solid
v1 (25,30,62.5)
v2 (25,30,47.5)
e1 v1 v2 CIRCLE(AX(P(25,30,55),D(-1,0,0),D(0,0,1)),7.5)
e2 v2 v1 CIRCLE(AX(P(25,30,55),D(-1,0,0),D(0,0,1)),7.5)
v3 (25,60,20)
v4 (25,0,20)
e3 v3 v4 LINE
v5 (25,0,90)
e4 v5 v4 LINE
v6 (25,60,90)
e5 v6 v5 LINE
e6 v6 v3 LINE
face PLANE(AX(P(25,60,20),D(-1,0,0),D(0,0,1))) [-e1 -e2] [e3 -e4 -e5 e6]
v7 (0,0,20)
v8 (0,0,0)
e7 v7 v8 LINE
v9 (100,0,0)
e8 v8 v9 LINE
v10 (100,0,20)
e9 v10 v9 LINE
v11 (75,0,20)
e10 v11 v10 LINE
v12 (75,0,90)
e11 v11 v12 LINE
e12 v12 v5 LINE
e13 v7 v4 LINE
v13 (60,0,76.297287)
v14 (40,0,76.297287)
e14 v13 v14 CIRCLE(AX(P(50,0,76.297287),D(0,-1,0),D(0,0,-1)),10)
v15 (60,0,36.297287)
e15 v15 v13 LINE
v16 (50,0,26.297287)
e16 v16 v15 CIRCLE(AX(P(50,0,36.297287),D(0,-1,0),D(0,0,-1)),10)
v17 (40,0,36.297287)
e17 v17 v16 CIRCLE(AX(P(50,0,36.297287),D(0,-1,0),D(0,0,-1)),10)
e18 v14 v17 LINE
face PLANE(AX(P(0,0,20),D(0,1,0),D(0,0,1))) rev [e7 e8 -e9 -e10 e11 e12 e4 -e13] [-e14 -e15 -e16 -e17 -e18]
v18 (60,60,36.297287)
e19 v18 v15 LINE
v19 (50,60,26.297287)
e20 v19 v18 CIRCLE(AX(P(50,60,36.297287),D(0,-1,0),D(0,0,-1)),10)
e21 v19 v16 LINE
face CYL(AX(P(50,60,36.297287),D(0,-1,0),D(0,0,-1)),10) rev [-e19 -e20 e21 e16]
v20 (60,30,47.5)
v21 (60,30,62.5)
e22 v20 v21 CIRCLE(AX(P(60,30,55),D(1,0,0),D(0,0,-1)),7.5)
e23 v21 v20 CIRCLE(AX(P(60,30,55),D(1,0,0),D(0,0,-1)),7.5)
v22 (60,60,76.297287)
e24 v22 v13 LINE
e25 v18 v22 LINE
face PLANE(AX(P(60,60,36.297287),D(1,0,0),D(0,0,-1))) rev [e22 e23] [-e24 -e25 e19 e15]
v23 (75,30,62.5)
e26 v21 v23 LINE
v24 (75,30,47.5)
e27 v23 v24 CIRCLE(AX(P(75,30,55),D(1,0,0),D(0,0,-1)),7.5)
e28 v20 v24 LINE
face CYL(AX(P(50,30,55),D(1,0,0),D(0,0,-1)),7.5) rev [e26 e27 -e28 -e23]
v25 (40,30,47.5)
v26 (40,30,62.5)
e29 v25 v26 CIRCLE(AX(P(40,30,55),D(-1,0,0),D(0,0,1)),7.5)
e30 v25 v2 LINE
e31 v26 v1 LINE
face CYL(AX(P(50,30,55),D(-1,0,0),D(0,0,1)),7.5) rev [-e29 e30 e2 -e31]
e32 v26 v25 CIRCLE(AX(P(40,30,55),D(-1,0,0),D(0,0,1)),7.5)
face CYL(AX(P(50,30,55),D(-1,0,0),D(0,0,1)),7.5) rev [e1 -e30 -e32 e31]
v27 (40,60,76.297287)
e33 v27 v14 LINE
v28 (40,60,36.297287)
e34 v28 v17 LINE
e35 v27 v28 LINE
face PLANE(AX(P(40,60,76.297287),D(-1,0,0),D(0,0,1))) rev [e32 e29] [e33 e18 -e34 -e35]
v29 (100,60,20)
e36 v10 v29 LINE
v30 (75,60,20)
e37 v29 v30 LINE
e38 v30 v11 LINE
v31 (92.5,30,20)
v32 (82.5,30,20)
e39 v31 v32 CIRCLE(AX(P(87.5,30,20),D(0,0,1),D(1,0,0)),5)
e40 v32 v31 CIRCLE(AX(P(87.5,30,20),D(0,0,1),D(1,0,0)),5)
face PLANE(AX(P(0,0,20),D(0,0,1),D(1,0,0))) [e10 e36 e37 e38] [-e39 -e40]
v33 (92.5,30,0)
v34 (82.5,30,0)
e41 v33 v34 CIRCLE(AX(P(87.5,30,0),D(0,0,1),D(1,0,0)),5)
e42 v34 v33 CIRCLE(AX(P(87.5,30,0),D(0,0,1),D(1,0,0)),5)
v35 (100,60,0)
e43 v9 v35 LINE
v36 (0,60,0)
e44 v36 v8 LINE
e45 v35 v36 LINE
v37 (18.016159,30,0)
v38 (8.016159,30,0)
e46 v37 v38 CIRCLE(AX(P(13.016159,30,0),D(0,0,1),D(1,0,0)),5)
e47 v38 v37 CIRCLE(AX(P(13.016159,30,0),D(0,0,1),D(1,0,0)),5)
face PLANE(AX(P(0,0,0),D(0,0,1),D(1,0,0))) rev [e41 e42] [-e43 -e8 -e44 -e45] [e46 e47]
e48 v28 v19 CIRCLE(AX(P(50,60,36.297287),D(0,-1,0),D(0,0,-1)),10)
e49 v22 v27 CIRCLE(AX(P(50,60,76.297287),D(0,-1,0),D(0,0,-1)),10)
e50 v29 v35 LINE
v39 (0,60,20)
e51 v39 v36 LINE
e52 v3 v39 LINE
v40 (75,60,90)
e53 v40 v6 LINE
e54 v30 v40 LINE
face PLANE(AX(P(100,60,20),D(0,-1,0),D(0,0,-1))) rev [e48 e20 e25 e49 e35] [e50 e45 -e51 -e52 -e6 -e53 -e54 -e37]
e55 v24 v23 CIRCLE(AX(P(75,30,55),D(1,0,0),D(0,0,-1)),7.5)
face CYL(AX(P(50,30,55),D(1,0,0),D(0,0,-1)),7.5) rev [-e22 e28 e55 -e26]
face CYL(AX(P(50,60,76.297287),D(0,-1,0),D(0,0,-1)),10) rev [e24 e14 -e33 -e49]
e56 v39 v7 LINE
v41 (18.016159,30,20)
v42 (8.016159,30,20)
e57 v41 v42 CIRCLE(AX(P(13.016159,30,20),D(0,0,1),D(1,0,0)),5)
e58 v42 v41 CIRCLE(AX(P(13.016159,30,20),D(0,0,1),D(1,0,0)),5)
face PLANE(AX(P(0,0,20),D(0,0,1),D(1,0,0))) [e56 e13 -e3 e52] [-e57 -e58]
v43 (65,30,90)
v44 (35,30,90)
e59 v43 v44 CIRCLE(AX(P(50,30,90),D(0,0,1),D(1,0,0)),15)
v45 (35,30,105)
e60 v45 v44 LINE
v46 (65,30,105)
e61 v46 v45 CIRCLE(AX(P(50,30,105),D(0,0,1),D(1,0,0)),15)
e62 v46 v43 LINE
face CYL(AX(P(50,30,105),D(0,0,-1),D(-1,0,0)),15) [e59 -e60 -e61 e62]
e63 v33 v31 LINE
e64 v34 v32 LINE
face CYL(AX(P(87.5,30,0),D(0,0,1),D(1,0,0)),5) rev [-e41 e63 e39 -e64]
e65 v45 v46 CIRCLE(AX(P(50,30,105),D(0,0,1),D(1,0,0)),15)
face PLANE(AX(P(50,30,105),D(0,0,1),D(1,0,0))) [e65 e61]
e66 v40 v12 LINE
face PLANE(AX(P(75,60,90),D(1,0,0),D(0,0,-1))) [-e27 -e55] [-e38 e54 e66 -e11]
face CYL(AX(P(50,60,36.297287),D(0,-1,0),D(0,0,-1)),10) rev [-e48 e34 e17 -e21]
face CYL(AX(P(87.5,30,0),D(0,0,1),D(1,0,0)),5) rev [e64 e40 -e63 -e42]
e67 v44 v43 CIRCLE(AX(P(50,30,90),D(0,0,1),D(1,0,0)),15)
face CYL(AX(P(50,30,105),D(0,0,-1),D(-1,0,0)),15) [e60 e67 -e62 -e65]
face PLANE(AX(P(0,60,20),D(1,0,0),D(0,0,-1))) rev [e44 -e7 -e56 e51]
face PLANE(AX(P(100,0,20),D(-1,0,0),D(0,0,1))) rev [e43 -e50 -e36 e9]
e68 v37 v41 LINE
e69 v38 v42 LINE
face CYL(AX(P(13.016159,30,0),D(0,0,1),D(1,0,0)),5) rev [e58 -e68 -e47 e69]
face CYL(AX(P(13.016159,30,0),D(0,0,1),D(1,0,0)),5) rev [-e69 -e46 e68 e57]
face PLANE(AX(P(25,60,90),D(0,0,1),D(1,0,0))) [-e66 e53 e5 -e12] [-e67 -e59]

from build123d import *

# Parameters (mm, degrees)
BASE_PLATE_SKETCH_W      = 100
BASE_PLATE_SKETCH_H      = 60
BASE_PLATE_DEPTH         = 20
UPRIGHT_BLOCK_DEPTH      = 60
TOP_SLOT_DEPTH           = 60
NOTCH_SKETCH_R           = 5
NOTCH_CUT_DEPTH          = 20
CROSS_HOLE_A_15_SKETCH_R = 7.5
CROSS_HOLE_A_15_DEPTH    = 25
CROSS_START              = -25
CROSS_HOLE_B_15_SKETCH_R = 7.5
CROSS_HOLE_B_15_DEPTH    = 25
PIN_BOSS_30_SKETCH_R     = 15
PIN_BOSS_30_DEPTH        = 15


with BuildPart() as part:
    # Base Plate Sketch → Base Plate (new body)
    with BuildSketch(Plane.XY):
        with Locations((50, 30)):
            Rectangle(BASE_PLATE_SKETCH_W, BASE_PLATE_SKETCH_H)
    extrude(amount=BASE_PLATE_DEPTH)

    # Upright Block Sketch → Upright Block (add)
    with BuildSketch(Plane.XZ):
        Polygon((50, 20), (25, 20), (25, 90), (75, 90), (75, 20), align=None)
    extrude(amount=-UPRIGHT_BLOCK_DEPTH)

    # Top Slot Sketch → Top Slot (cut)
    with BuildSketch(Plane.XZ):
        with BuildLine():
            Line((40, 76.29728725), (40, 36.29728725))
            ThreePointArc((40, 36.29728725), (50, 26.29728725), (60, 36.29728725))
            Line((60, 36.29728725), (60, 76.29728725))
            ThreePointArc((60, 76.29728725), (50, 86.29728725), (40, 76.29728725))
        make_face()
    extrude(amount=-TOP_SLOT_DEPTH, mode=Mode.SUBTRACT)

    # Notch Sketch → Notch Cut (cut)
    with BuildSketch(Plane.XY.offset(20)):
        with Locations((87.5, 30)):
            Circle(NOTCH_SKETCH_R)
        with Locations((13.016158592, 30)):
            Circle(NOTCH_SKETCH_R)
    extrude(amount=-NOTCH_CUT_DEPTH, mode=Mode.SUBTRACT)

    # Cross Hole A Ø15 Sketch → Cross Hole A Ø15 (cut)
    with BuildSketch(Plane(origin=(75, 0, 0), x_dir=(0, 0, -1), z_dir=(1, 0, 0))):
        with Locations((-55, 30)):
            Circle(CROSS_HOLE_A_15_SKETCH_R)
    extrude(amount=-CROSS_HOLE_A_15_DEPTH, mode=Mode.SUBTRACT)

    # Cross Hole B Ø15 Sketch → Cross Hole B Ø15 (cut)
    with BuildSketch(Plane.ZY.offset(-25).offset(CROSS_START)):
        with Locations(Location((55, 30, 0), (0, 0, 180))):
            Circle(CROSS_HOLE_B_15_SKETCH_R)
    extrude(amount=CROSS_HOLE_B_15_DEPTH, mode=Mode.SUBTRACT)

    # Pin Boss Ø30 Sketch → Pin Boss Ø30 (add)
    with BuildSketch(Plane.XY.offset(90)):
        with Locations((50, 30)):
            Circle(PIN_BOSS_30_SKETCH_R)
    extrude(amount=PIN_BOSS_30_DEPTH)


solid = part.part
